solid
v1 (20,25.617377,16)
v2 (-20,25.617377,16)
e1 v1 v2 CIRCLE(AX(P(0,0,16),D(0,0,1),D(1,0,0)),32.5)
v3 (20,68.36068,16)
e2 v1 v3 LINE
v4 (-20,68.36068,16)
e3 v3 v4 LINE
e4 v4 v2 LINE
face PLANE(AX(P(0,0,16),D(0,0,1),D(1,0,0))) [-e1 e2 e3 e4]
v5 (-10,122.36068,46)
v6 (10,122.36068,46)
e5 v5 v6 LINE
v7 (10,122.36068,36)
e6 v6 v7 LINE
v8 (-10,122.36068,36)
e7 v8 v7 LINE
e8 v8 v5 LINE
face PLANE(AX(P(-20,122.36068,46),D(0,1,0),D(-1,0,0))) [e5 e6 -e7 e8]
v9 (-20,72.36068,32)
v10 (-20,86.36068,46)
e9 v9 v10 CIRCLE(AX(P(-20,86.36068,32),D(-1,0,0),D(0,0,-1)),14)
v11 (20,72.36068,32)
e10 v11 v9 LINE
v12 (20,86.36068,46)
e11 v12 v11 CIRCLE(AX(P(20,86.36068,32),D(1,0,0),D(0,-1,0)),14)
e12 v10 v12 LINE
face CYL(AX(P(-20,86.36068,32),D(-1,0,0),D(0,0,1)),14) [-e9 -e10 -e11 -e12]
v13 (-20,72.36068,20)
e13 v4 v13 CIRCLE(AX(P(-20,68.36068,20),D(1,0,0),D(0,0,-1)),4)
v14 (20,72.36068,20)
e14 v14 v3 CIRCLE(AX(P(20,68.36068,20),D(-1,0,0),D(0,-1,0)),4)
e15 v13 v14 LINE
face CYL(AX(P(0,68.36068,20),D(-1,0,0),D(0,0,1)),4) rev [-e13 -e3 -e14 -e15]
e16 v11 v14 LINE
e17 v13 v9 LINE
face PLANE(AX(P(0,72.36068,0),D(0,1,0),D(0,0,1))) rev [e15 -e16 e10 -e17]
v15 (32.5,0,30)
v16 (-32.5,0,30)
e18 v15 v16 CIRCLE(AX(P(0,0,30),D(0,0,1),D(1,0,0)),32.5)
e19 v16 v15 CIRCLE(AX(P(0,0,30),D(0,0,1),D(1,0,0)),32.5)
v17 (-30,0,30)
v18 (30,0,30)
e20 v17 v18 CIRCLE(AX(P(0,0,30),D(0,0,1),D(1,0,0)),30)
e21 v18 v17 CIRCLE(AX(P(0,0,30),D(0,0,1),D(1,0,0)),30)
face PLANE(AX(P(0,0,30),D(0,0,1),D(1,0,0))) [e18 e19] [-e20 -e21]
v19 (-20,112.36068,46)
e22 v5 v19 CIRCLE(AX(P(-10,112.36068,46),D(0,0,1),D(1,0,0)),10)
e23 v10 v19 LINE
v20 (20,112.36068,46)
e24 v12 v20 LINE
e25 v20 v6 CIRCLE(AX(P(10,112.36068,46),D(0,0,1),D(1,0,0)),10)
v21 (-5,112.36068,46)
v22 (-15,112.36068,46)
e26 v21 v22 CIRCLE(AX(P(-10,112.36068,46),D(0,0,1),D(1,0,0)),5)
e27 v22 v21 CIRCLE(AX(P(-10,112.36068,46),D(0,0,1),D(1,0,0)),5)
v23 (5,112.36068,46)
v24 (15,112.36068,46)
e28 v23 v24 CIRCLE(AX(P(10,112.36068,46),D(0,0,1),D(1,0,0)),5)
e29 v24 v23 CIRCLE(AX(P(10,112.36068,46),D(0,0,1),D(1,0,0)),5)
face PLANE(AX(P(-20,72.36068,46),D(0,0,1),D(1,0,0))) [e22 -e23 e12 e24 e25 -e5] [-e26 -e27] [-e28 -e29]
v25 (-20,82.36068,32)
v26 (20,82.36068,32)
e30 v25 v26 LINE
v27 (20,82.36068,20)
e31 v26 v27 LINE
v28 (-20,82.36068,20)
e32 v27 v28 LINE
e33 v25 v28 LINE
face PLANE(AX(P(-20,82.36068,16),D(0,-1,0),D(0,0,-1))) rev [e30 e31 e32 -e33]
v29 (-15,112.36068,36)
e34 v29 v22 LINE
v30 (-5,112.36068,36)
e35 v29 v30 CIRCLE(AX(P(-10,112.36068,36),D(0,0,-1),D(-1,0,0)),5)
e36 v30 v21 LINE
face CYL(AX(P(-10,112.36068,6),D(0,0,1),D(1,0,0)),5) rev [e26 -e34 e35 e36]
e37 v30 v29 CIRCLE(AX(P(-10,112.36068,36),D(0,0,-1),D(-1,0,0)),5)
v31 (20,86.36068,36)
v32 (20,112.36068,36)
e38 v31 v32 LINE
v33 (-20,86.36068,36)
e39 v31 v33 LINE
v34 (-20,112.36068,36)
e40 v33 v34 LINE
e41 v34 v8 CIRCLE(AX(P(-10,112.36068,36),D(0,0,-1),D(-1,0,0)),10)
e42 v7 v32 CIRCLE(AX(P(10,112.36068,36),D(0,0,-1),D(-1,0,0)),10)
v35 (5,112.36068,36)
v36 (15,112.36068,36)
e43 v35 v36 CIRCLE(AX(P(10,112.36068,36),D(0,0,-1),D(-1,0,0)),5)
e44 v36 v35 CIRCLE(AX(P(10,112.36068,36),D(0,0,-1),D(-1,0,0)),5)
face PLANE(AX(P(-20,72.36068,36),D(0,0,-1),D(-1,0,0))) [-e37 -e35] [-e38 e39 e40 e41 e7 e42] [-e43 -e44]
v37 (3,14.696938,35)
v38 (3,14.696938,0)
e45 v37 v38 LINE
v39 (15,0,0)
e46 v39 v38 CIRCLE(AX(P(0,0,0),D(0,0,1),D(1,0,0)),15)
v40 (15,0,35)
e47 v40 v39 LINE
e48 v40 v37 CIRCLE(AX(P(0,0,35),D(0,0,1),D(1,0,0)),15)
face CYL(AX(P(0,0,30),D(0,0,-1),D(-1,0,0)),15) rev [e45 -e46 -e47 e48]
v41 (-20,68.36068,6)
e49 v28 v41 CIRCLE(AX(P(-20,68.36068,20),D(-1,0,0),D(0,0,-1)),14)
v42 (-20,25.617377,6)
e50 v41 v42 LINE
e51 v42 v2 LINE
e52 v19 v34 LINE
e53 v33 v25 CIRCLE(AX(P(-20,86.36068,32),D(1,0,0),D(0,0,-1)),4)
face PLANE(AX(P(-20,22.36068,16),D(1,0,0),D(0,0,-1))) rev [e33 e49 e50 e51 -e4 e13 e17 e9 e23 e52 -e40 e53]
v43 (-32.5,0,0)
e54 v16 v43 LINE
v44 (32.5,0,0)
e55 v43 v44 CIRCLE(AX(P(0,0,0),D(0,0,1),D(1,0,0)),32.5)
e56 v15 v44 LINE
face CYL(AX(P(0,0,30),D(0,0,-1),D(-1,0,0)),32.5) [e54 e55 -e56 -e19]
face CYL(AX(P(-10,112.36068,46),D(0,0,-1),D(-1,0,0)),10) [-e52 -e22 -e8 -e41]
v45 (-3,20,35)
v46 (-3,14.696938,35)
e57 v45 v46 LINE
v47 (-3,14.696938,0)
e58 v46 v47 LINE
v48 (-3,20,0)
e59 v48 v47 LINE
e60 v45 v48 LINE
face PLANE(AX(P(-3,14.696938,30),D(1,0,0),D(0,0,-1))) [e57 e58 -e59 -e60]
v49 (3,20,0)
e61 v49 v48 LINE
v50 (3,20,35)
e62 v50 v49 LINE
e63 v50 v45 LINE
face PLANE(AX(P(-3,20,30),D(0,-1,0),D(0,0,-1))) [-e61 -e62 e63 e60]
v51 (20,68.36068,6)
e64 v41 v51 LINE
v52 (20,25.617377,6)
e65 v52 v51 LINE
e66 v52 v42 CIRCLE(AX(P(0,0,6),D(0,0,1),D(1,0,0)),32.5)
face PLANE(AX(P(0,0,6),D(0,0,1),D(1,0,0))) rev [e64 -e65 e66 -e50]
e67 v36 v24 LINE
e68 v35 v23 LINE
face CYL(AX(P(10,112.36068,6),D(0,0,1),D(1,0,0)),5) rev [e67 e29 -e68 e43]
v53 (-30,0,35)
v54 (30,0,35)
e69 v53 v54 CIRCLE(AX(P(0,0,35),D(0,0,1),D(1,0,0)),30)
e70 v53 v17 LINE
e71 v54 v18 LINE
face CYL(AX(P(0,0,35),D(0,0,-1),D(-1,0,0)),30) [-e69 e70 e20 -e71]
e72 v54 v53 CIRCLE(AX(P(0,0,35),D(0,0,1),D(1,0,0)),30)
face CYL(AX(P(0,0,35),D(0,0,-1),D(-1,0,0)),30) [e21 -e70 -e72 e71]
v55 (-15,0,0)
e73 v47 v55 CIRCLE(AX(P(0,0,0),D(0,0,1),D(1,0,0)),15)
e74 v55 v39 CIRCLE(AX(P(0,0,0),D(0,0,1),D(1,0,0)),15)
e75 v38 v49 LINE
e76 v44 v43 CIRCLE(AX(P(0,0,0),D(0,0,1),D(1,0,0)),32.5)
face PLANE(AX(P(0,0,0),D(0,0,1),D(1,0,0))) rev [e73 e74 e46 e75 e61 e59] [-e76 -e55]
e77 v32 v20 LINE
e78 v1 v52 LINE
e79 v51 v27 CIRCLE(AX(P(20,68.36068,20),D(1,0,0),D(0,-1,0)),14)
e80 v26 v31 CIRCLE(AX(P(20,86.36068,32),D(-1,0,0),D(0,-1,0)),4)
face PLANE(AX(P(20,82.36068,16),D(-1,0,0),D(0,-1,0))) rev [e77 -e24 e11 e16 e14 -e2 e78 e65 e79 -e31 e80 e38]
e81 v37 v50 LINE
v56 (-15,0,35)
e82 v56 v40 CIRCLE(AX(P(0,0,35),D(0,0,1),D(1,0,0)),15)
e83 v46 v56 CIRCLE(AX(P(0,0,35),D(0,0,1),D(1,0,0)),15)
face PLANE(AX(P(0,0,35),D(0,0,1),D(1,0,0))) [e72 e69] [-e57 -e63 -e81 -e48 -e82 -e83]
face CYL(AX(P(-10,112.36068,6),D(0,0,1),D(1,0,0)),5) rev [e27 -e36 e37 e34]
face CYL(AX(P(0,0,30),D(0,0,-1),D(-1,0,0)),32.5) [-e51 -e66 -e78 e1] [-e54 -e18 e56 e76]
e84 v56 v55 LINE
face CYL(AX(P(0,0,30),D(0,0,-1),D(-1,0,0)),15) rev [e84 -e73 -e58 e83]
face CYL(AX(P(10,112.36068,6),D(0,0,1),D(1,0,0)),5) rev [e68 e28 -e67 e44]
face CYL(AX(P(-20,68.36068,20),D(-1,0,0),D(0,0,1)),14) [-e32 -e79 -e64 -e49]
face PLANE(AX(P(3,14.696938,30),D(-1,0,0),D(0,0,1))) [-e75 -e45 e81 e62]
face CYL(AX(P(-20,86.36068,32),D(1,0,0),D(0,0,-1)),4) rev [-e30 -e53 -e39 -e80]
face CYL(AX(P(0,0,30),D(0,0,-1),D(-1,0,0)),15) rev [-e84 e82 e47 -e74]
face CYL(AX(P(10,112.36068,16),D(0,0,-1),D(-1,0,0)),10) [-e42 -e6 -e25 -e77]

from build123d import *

# Parameters (mm, degrees)
KEYED_HUB_PROFILE_R             = 32.5
KEYED_HUB_65_DEPTH              = 30
HUB_SHOULDER_PROFILE_R          = 30
HUB_SHOULDER_RING_60_DEPTH      = 5
SUPPORT_ARM_PROFILE_W           = 40
SUPPORT_ARM_PROFILE_H           = 60
SUPPORT_ARM_DEPTH               = 10
ARM_JOGGLE_PROFILE_W            = 40
ARM_JOGGLE_PROFILE_H            = 40
ARM_JOGGLE_DEPTH                = 10
MOUNTING_FLANGE_PROFILE_W       = 10
MOUNTING_FLANGE_PROFILE_H       = 50
MOUNTING_FLANGE_DEPTH           = 40
FLANGE_CORNER_FILLETS_R10_R     = 10
ARM_OUTER_BEND_FILLET_R14_R     = 14
JOGGLE_OUTER_BEND_FILLET_R14_R  = 14
ARM_JOGGLE_INNER_FILLET_R4_R    = 4
ARM_FLANGE_INNER_FILLET_R4_R    = 4
FLANGE_MOUNTING_HOLES_PROFILE_R = 5
FLANGE_MOUNTING_HOLES_2X_DEPTH  = 40


with BuildPart() as part:
    # Keyed Hub Profile → Keyed Hub Ø65 (new body)
    with BuildSketch(Plane.XY):
        Circle(KEYED_HUB_PROFILE_R)
        with BuildLine():
            Line((-3, 20), (3, 20))
            Line((3, 20), (3, 14.696938457))
            ThreePointArc((3, 14.696938457), (0, -15), (-3, 14.696938457))
            Line((-3, 14.696938457), (-3, 20))
        make_face(mode=Mode.SUBTRACT)
    extrude(amount=KEYED_HUB_65_DEPTH)

    # Hub Shoulder Profile → Hub Shoulder Ring Ø60 (add)
    with BuildSketch(Plane.XY.offset(30)):
        Circle(HUB_SHOULDER_PROFILE_R)
        with BuildLine():
            Line((-3, 14.696938457), (-3, 20))
            Line((-3, 20), (3, 20))
            Line((3, 20), (3, 14.696938457))
            ThreePointArc((3, 14.696938457), (0, -15), (-3, 14.696938457))
        make_face(mode=Mode.SUBTRACT)
    extrude(amount=HUB_SHOULDER_RING_60_DEPTH)

    # Support Arm Profile → Support Arm (add)
    with BuildSketch(Plane.XY.offset(6)):
        with Locations((0, 52.360679775)):
            Rectangle(SUPPORT_ARM_PROFILE_W, SUPPORT_ARM_PROFILE_H)
    extrude(amount=SUPPORT_ARM_DEPTH)

    # Arm Joggle Profile → Arm Joggle (add)
    with BuildSketch(Plane(origin=(0, 82.360679775, 0), x_dir=(1, 0, 0), z_dir=(0, 1, 0))):
        with Locations((0, -26)):
            Rectangle(ARM_JOGGLE_PROFILE_W, ARM_JOGGLE_PROFILE_H)
    extrude(amount=-ARM_JOGGLE_DEPTH)

    # Mounting Flange Profile → Mounting Flange (add)
    with BuildSketch(Plane(origin=(20, 0, 0), x_dir=(0, 0, -1), z_dir=(1, 0, 0))):
        with Locations((-41, 97.360679775)):
            Rectangle(MOUNTING_FLANGE_PROFILE_W, MOUNTING_FLANGE_PROFILE_H)
    extrude(amount=-MOUNTING_FLANGE_DEPTH)

    # Flange Corner Fillets R10
    flange_corner_fillets_r10_edges = [part.edges().sort_by_distance(p)[0] for p in [
        (20, 122.360679775, 41),
        (-20, 122.360679775, 41),
    ]]
    fillet(flange_corner_fillets_r10_edges, radius=FLANGE_CORNER_FILLETS_R10_R)

    # Arm Outer Bend Fillet R14
    arm_outer_bend_fillet_r14_edges = [part.edges().sort_by_distance(p)[0] for p in [
        (0, 82.360679775, 6),
    ]]
    fillet(arm_outer_bend_fillet_r14_edges, radius=ARM_OUTER_BEND_FILLET_R14_R)

    # Joggle Outer Bend Fillet R14
    joggle_outer_bend_fillet_r14_edges = [part.edges().sort_by_distance(p)[0] for p in [
        (0, 72.360679775, 46),
    ]]
    fillet(joggle_outer_bend_fillet_r14_edges, radius=JOGGLE_OUTER_BEND_FILLET_R14_R)

    # Arm-Joggle Inner Fillet R4
    arm_joggle_inner_fillet_r4_edges = [part.edges().sort_by_distance(p)[0] for p in [
        (0, 72.360679775, 16),
    ]]
    fillet(arm_joggle_inner_fillet_r4_edges, radius=ARM_JOGGLE_INNER_FILLET_R4_R)

    # Arm-Flange Inner Fillet R4
    arm_flange_inner_fillet_r4_edges = [part.edges().sort_by_distance(p)[0] for p in [
        (0, 82.360679775, 36),
    ]]
    fillet(arm_flange_inner_fillet_r4_edges, radius=ARM_FLANGE_INNER_FILLET_R4_R)

    # Flange Mounting Holes Profile → Flange Mounting Holes 2x (cut)
    with BuildSketch(Plane.XY.offset(46)):
        with Locations((-10, 112.360679775)):
            Circle(FLANGE_MOUNTING_HOLES_PROFILE_R)
        with Locations((10, 112.360679775)):
            Circle(FLANGE_MOUNTING_HOLES_PROFILE_R)
    extrude(amount=-FLANGE_MOUNTING_HOLES_2X_DEPTH, mode=Mode.SUBTRACT)


solid = part.part
